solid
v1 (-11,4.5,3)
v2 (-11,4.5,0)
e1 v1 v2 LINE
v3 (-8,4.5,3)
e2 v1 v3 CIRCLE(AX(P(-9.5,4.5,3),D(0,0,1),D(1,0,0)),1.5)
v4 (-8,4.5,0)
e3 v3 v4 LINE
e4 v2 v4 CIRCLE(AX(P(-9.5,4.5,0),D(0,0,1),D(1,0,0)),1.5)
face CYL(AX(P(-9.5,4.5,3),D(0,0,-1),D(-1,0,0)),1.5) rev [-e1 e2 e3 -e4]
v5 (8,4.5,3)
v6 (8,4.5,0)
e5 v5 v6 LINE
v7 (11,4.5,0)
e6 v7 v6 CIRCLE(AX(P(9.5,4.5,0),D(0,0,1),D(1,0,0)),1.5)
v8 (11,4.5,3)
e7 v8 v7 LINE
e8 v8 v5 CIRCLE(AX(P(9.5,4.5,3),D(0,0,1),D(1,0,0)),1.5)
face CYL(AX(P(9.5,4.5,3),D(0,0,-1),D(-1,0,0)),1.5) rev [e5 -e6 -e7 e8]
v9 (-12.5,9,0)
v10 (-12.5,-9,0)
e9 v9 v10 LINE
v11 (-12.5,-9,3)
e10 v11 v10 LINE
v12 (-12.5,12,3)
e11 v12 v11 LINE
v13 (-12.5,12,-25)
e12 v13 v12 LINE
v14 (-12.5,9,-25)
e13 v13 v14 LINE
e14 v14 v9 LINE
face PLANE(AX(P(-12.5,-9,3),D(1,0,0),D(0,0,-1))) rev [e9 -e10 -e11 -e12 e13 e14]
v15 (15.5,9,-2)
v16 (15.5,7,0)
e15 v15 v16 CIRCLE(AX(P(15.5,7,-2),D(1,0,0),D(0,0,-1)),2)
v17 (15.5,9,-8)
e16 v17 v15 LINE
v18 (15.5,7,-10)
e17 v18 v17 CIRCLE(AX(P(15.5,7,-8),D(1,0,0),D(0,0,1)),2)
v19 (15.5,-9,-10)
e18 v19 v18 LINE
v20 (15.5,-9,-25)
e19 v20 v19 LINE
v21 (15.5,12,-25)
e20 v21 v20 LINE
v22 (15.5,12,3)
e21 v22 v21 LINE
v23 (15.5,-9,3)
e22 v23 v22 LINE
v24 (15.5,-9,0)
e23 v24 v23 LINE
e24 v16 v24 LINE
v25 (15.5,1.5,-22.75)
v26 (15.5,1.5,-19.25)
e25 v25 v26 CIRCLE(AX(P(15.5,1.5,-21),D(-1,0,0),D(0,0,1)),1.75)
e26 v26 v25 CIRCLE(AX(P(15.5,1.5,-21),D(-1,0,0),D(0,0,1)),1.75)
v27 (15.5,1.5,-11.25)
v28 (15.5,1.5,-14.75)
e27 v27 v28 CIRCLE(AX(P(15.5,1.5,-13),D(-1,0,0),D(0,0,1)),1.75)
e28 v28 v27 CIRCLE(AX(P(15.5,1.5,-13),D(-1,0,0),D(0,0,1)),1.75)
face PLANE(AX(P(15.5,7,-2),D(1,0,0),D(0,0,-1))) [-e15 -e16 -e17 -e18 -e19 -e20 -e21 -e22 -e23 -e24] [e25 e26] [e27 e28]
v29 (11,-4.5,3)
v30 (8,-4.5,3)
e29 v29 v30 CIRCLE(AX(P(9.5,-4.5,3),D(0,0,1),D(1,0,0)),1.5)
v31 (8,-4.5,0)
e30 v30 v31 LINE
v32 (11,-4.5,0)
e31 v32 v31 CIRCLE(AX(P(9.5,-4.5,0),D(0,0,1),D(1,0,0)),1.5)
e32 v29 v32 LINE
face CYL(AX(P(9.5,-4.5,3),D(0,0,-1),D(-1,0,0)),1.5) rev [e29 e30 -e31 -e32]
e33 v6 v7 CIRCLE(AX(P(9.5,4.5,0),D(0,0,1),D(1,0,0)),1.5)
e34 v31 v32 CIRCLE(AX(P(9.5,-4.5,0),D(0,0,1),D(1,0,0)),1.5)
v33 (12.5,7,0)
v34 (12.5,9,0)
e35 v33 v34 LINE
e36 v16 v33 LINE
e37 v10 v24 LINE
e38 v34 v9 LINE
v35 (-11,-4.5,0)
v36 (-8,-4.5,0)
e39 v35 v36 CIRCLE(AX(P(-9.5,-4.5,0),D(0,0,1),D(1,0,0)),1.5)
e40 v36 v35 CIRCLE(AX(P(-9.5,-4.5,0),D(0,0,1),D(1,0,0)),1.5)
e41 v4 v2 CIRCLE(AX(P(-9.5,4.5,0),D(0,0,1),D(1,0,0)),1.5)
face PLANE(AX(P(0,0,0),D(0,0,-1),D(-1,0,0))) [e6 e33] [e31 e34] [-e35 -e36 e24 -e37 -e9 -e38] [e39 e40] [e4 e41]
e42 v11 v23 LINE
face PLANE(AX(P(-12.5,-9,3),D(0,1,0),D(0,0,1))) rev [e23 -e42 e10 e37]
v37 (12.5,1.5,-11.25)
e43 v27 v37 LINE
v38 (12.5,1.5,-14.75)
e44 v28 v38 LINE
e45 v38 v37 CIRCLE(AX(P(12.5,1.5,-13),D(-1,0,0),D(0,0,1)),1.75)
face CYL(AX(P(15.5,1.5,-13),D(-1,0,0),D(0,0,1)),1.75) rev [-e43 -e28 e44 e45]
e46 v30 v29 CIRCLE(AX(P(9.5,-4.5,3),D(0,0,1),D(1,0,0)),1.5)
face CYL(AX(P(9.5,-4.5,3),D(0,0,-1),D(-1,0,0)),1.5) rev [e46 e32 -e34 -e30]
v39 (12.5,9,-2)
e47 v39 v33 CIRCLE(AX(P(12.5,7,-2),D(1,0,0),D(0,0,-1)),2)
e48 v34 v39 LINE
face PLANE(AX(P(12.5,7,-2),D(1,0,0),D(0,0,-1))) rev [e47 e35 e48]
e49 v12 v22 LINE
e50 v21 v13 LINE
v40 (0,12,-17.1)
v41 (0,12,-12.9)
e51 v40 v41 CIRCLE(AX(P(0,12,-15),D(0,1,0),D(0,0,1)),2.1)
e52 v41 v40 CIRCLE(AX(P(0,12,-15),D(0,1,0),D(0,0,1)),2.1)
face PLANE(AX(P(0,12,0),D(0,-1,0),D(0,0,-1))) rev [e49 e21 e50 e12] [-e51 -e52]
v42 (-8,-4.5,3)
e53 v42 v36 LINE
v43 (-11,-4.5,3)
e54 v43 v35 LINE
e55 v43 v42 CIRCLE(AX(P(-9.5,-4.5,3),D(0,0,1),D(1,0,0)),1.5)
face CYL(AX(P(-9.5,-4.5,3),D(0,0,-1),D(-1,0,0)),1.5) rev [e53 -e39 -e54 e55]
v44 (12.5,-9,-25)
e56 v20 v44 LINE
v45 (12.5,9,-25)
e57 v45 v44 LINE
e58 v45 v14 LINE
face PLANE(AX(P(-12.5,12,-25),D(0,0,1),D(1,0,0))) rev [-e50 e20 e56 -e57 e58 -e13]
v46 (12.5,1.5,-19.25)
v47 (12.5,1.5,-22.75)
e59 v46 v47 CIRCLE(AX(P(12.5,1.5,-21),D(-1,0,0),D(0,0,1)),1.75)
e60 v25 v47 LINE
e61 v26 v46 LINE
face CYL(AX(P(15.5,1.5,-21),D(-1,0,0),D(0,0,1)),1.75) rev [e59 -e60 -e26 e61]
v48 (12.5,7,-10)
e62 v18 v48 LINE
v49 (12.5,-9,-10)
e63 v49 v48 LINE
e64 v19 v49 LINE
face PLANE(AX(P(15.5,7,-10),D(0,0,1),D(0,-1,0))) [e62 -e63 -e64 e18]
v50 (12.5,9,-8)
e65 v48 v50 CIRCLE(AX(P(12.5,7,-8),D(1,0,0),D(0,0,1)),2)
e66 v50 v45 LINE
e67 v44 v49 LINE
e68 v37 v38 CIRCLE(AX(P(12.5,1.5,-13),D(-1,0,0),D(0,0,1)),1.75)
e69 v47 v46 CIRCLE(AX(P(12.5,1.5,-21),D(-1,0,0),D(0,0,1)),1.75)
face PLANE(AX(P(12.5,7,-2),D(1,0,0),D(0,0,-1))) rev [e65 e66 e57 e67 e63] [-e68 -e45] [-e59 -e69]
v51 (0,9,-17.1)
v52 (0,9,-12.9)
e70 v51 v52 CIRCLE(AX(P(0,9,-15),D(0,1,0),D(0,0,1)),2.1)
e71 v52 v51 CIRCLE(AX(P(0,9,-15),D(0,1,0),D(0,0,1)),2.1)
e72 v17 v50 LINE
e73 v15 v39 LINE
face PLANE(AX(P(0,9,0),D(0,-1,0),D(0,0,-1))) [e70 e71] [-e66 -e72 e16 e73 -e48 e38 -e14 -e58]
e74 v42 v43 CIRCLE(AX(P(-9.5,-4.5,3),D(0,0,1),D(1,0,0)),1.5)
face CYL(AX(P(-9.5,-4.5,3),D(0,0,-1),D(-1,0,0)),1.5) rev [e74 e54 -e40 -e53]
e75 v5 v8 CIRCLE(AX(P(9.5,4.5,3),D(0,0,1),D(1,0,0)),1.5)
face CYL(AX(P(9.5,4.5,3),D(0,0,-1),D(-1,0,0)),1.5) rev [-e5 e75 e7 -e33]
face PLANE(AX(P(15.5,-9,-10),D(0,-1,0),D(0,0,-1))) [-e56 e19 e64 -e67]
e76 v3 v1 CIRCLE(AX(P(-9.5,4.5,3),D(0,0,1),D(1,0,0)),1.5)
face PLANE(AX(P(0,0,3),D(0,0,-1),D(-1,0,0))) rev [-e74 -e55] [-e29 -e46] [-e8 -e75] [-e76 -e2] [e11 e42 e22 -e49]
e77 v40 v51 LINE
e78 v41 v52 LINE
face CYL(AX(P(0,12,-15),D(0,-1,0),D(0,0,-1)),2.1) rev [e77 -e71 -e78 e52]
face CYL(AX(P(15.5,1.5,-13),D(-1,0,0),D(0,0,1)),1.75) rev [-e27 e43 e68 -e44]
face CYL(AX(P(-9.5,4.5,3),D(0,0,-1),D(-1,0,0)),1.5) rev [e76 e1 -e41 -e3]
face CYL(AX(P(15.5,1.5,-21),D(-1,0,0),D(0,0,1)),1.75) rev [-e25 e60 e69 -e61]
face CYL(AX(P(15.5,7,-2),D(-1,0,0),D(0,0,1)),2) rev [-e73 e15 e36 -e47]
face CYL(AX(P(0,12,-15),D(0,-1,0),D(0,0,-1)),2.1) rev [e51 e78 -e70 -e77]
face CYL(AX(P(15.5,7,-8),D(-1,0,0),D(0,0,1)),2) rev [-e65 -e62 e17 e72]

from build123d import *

# Parameters (mm, degrees)
SKETCH1_W           = 25
SKETCH1_H           = 18
SKETCH1_R           = 1.5
BOSS_EXTRUDE1_DEPTH = 3
SKETCH2_W           = 25
SKETCH2_H           = 28
SKETCH2_R           = 2.1
BOSS_EXTRUDE2_DEPTH = 3
SKETCH3_R           = 1.75
BOSS_EXTRUDE3_DEPTH = 3


with BuildPart() as part:
    # Sketch1 → Boss-Extrude1 (new body)
    with BuildSketch(Plane.XY):
        Rectangle(SKETCH1_W, SKETCH1_H)
        with Locations((-9.5, 4.5)):
            Circle(SKETCH1_R, mode=Mode.SUBTRACT)
        with Locations((9.5, 4.5)):
            Circle(SKETCH1_R, mode=Mode.SUBTRACT)
        with Locations((9.5, -4.5)):
            Circle(SKETCH1_R, mode=Mode.SUBTRACT)
        with Locations((-9.5, -4.5)):
            Circle(SKETCH1_R, mode=Mode.SUBTRACT)
    extrude(amount=BOSS_EXTRUDE1_DEPTH)

    # Sketch2 → Boss-Extrude2 (add)
    with BuildSketch(Plane(origin=(0, 9, 0), x_dir=(1, 0, 0), z_dir=(0, 1, 0))):
        with Locations((0, 11)):
            Rectangle(SKETCH2_W, SKETCH2_H)
        with Locations(Location((0, 15, 0), (0, 0, 270))):
            Circle(SKETCH2_R, mode=Mode.SUBTRACT)
    extrude(amount=BOSS_EXTRUDE2_DEPTH)

    # Sketch3 → Boss-Extrude3 (add)
    with BuildSketch(Plane.ZY.offset(-12.5)):
        with BuildLine():
            Line((0, -9), (0, 7))
            ThreePointArc((0, 7), (-0.585786438, 8.414213562), (-2, 9))
            Line((-2, 9), (-8, 9))
            ThreePointArc((-8, 9), (-9.414213562, 8.414213562), (-10, 7))
            Line((-10, 7), (-10, -9))
            Line((-10, -9), (-25, -9))
            Line((-25, -9), (-25, 12))
            Line((-25, 12), (3, 12))
            Line((3, 12), (3, -9))
            Line((3, -9), (0, -9))
        make_face()
        with Locations((-21, 1.5)):
            Circle(SKETCH3_R, mode=Mode.SUBTRACT)
        with Locations((-13, 1.5)):
            Circle(SKETCH3_R, mode=Mode.SUBTRACT)
    extrude(amount=-BOSS_EXTRUDE3_DEPTH)


solid = part.part
